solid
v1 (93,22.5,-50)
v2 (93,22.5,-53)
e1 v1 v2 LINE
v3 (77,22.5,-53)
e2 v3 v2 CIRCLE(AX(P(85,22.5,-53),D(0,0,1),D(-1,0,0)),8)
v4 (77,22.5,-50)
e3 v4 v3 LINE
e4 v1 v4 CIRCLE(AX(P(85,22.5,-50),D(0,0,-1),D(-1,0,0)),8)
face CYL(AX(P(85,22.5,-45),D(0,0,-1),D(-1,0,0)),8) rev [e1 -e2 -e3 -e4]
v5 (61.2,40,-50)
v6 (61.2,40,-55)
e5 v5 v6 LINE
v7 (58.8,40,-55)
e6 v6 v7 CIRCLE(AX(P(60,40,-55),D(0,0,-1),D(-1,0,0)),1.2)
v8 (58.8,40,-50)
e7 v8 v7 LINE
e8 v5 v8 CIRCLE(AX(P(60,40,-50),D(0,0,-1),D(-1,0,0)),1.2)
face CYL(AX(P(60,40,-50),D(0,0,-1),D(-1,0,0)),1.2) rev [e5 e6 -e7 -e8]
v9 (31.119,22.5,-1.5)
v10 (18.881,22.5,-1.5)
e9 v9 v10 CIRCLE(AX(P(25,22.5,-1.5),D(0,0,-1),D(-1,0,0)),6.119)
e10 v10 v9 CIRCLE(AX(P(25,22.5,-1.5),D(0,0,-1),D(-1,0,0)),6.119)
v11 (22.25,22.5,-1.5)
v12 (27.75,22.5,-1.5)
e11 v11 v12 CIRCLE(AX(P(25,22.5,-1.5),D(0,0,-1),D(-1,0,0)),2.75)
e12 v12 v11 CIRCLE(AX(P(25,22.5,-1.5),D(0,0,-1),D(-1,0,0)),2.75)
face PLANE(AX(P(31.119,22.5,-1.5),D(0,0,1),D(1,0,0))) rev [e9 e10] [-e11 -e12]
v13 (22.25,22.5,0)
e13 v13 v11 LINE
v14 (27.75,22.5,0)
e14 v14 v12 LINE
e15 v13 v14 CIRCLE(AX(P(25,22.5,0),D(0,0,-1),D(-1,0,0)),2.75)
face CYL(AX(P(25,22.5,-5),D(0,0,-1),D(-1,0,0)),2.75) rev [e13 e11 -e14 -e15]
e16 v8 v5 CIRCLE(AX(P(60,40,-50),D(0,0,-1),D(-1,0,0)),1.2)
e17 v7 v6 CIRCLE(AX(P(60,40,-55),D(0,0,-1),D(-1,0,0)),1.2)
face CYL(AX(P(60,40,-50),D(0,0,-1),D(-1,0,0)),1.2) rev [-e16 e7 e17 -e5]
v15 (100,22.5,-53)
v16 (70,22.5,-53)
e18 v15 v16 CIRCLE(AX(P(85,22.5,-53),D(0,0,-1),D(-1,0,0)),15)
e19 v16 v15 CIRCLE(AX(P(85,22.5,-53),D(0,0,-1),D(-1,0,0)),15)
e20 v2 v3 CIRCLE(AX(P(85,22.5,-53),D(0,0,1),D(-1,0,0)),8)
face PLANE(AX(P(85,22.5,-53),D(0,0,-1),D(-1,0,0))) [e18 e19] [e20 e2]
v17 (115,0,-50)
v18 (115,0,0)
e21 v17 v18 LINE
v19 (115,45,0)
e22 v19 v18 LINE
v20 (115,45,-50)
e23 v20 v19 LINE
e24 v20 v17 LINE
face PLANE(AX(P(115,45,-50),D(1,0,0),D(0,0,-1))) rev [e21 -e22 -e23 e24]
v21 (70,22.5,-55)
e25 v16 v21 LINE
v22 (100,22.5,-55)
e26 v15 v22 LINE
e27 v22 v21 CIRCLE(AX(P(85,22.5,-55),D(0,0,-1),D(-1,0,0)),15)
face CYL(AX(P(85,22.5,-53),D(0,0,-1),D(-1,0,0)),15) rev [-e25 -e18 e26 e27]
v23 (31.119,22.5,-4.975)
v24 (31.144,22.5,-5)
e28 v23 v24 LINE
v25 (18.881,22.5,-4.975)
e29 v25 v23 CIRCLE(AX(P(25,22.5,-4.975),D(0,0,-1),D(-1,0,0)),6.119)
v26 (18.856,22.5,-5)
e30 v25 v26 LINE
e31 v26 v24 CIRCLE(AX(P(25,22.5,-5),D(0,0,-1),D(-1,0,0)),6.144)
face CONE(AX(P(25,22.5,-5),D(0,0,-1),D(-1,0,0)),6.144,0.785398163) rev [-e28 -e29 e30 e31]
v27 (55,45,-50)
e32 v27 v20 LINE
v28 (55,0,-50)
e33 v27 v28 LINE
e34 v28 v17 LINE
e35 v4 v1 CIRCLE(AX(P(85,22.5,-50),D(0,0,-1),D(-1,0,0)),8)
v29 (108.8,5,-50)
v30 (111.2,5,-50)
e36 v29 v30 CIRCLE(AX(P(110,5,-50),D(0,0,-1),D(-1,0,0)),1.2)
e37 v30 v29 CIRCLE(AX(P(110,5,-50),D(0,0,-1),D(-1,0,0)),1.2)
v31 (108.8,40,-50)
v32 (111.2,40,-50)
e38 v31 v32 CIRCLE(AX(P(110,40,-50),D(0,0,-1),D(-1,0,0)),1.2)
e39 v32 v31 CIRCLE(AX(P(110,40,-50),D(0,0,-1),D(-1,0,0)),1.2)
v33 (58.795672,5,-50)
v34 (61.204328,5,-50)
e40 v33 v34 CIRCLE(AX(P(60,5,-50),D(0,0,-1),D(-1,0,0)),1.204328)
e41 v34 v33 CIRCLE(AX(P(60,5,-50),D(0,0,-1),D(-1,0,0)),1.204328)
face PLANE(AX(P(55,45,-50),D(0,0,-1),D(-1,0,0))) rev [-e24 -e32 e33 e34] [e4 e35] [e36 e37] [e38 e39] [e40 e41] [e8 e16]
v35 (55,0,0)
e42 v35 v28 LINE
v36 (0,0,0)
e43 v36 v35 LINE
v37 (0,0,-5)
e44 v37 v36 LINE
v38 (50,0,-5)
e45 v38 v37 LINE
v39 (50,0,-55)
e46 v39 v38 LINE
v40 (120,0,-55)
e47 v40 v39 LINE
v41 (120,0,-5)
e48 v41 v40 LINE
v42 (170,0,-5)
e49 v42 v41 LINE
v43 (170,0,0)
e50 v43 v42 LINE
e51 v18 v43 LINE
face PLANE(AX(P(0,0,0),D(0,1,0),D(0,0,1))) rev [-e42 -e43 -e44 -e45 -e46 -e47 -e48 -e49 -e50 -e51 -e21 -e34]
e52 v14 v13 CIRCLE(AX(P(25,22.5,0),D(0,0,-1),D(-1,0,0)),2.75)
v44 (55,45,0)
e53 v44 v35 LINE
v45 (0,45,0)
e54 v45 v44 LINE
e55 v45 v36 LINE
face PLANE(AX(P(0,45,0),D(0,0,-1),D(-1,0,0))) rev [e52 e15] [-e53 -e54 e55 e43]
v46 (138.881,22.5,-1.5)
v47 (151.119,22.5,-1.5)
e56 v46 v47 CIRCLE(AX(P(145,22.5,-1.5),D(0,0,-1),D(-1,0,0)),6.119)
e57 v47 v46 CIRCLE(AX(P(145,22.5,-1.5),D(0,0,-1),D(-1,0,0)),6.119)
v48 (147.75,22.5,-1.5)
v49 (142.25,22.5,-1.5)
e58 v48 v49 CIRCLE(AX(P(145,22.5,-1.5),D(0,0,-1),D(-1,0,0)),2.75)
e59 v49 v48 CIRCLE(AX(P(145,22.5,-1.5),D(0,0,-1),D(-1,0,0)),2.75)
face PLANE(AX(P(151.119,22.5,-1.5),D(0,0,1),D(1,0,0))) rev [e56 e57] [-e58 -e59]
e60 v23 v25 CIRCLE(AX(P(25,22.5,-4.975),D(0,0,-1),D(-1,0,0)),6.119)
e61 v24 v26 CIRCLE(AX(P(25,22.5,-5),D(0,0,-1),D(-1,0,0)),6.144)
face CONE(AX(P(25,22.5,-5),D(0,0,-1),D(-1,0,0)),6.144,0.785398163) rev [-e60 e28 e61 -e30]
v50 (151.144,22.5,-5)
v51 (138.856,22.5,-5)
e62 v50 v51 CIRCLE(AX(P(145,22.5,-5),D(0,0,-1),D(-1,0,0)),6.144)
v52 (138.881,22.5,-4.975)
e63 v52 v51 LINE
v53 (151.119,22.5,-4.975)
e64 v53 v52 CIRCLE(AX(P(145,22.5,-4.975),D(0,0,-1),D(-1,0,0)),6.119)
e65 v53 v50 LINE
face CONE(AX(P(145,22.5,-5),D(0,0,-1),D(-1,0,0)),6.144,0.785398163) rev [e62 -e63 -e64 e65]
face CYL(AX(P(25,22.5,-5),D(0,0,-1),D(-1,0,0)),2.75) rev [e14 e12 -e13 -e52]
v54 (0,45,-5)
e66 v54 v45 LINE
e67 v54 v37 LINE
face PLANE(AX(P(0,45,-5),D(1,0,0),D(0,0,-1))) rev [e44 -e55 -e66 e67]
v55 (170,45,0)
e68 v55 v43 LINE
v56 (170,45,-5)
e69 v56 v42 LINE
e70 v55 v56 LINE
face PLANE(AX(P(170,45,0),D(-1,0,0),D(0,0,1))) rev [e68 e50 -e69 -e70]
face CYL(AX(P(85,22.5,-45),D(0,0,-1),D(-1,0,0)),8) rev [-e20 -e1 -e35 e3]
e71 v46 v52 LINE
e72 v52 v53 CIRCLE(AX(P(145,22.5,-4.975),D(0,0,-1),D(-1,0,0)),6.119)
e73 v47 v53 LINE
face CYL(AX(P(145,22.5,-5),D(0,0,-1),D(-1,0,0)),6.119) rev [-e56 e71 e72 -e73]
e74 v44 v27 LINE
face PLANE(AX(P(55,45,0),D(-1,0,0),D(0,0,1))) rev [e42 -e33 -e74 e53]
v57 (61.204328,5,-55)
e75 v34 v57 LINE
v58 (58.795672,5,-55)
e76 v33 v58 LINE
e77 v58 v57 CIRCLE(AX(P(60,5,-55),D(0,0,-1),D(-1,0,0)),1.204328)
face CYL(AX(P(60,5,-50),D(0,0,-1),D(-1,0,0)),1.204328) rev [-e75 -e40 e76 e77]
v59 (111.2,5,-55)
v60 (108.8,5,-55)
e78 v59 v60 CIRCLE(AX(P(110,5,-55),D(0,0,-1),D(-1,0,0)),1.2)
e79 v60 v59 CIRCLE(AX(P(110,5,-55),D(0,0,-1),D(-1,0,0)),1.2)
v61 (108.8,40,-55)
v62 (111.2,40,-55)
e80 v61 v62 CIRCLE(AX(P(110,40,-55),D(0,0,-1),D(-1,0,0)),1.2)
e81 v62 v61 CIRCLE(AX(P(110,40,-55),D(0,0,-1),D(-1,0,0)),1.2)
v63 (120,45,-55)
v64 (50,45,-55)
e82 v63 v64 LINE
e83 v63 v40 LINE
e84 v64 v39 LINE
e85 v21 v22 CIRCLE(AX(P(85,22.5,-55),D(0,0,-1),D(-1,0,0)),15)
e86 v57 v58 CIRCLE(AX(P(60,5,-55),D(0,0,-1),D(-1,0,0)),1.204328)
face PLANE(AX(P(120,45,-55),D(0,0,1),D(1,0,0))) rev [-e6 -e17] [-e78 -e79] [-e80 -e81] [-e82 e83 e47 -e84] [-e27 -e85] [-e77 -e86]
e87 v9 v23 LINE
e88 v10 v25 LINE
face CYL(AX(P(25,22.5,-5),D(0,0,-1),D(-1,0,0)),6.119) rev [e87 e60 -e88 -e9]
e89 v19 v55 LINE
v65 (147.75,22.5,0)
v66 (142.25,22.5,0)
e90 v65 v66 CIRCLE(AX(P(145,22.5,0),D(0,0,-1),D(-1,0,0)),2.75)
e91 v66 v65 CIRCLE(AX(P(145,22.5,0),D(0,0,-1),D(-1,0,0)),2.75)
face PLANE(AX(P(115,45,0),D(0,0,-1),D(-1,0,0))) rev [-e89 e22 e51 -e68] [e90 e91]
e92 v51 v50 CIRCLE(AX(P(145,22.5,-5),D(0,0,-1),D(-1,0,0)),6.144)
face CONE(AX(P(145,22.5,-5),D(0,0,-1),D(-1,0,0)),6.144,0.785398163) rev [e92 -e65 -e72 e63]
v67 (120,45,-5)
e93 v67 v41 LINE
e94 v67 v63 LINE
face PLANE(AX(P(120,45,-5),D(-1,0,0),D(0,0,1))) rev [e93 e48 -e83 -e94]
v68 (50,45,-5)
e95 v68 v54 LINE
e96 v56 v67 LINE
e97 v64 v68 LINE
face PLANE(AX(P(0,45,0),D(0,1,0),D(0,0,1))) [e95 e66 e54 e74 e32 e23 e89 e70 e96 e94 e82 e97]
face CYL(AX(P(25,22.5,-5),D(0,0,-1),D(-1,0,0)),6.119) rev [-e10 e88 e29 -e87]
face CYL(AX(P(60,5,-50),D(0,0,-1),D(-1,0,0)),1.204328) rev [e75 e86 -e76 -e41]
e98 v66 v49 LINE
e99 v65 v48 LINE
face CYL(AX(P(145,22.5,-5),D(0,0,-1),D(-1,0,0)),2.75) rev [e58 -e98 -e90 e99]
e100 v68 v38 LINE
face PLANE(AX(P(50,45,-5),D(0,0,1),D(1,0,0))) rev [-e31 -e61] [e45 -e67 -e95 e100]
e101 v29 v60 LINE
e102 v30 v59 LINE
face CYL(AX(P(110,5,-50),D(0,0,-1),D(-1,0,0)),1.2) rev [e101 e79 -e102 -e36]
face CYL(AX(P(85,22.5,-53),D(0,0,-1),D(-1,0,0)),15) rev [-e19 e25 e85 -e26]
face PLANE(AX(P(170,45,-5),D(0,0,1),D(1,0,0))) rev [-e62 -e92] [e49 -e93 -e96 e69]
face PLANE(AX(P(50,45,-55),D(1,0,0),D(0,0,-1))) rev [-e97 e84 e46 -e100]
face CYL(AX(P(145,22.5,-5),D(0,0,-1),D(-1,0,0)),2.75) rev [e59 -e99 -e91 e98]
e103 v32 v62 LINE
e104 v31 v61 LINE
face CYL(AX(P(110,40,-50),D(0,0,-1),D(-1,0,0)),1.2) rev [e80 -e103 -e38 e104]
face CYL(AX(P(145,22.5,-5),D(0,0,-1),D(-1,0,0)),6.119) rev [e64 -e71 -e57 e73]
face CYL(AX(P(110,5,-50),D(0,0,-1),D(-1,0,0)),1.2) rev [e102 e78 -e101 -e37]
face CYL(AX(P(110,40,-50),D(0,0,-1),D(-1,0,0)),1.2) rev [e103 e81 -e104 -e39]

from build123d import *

# Parameters (mm, degrees)
BOSS_EXTRUDE3_DEPTH                    = 45
CBORE_FOR_M5_HEX_CAP_SCREW1_AT_2_COUNT = 2
CBORE_FOR_M5_HEX_CAP_SCREW1_AT_2_PITCH = 120
CUT_EXTRUDE1_DEPTH                     = 10
SKETCH13_R                             = 15
CUT_EXTRUDE2_DEPTH                     = 2
SKETCH14_R                             = 1.204328259
SKETCH14_R_2                           = 1.2
CUT_EXTRUDE3_DEPTH                     = 5


with BuildPart() as part:
    # Sketch7 → Boss-Extrude3 (new body)
    with BuildSketch(Plane(origin=(0, 0, 0), x_dir=(1, 0, 0), z_dir=(0, 1, 0))):
        Polygon((0, 0), (55, 0), (55, 50), (115, 50), (115, 0), (170, 0), (170, 5), (120, 5), (120, 55), (50, 55), (50, 5), (0, 5), align=None)
    extrude(amount=BOSS_EXTRUDE3_DEPTH)

    # Sketch10 → CBORE for M5 Hex Cap Screw1 (revolve, cut)
    with BuildSketch(Plane(origin=(145, 22.5, -5), x_dir=(0, 1, 0), z_dir=(1, 0, 0))):
        Polygon((0, 0), (0, 5), (2.75, 5), (2.75, 3.5), (6.119, 3.5), (6.119, 0.025), (6.144, 0), align=None)
    cbore_for_m5_hex_cap_screw1 = revolve(axis=Axis((145, 22.5, -11.35), (0, 0, 1)), mode=Mode.SUBTRACT)

    # CBORE for M5 Hex Cap Screw1 at 2: CBORE for M5 Hex Cap Screw1 ×2
    with Locations(*[(-i * CBORE_FOR_M5_HEX_CAP_SCREW1_AT_2_PITCH, 0, 0) for i in range(1, CBORE_FOR_M5_HEX_CAP_SCREW1_AT_2_COUNT)]):
        add(cbore_for_m5_hex_cap_screw1, mode=Mode.SUBTRACT)

    # Sketch12 → Cut-Extrude1 (cut)
    with BuildSketch(Plane(origin=(0, 0, -55), x_dir=(-1, 0, 0), z_dir=(0, 0, -1))):
        with BuildLine():
            ThreePointArc((-77, 22.5), (-82.745606781, 30.175787335), (-91.729427803, 26.826060731))
            Line((-91.729427803, 26.826060731), (-78.270572197, 18.173939269))
            ThreePointArc((-78.270572197, 18.173939269), (-77.324212665, 20.245606781), (-77, 22.5))
        make_face()
        with BuildLine():
            Line((-78.270572197, 18.173939269), (-91.729427803, 26.826060731))
            ThreePointArc((-91.729427803, 26.826060731), (-89.326060731, 15.770572197), (-78.270572197, 18.173939269))
        make_face()
    extrude(amount=-CUT_EXTRUDE1_DEPTH, mode=Mode.SUBTRACT)

    # Sketch13 → Cut-Extrude2 (cut)
    with BuildSketch(Plane(origin=(0, 0, -55), x_dir=(-1, 0, 0), z_dir=(0, 0, -1))):
        with Locations((-85, 22.5)):
            Circle(SKETCH13_R)
    extrude(amount=-CUT_EXTRUDE2_DEPTH, mode=Mode.SUBTRACT)

    # Sketch14 → Cut-Extrude3 (cut)
    with BuildSketch(Plane(origin=(0, 0, -55), x_dir=(-1, 0, 0), z_dir=(0, 0, -1))):
        with Locations((-60, 5)):
            Circle(SKETCH14_R)
        with Locations((-60, 40)):
            Circle(SKETCH14_R_2)
        with Locations((-110, 5)):
            Circle(SKETCH14_R_2)
        with Locations((-110, 40)):
            Circle(SKETCH14_R_2)
    extrude(amount=-CUT_EXTRUDE3_DEPTH, mode=Mode.SUBTRACT)


solid = part.part
